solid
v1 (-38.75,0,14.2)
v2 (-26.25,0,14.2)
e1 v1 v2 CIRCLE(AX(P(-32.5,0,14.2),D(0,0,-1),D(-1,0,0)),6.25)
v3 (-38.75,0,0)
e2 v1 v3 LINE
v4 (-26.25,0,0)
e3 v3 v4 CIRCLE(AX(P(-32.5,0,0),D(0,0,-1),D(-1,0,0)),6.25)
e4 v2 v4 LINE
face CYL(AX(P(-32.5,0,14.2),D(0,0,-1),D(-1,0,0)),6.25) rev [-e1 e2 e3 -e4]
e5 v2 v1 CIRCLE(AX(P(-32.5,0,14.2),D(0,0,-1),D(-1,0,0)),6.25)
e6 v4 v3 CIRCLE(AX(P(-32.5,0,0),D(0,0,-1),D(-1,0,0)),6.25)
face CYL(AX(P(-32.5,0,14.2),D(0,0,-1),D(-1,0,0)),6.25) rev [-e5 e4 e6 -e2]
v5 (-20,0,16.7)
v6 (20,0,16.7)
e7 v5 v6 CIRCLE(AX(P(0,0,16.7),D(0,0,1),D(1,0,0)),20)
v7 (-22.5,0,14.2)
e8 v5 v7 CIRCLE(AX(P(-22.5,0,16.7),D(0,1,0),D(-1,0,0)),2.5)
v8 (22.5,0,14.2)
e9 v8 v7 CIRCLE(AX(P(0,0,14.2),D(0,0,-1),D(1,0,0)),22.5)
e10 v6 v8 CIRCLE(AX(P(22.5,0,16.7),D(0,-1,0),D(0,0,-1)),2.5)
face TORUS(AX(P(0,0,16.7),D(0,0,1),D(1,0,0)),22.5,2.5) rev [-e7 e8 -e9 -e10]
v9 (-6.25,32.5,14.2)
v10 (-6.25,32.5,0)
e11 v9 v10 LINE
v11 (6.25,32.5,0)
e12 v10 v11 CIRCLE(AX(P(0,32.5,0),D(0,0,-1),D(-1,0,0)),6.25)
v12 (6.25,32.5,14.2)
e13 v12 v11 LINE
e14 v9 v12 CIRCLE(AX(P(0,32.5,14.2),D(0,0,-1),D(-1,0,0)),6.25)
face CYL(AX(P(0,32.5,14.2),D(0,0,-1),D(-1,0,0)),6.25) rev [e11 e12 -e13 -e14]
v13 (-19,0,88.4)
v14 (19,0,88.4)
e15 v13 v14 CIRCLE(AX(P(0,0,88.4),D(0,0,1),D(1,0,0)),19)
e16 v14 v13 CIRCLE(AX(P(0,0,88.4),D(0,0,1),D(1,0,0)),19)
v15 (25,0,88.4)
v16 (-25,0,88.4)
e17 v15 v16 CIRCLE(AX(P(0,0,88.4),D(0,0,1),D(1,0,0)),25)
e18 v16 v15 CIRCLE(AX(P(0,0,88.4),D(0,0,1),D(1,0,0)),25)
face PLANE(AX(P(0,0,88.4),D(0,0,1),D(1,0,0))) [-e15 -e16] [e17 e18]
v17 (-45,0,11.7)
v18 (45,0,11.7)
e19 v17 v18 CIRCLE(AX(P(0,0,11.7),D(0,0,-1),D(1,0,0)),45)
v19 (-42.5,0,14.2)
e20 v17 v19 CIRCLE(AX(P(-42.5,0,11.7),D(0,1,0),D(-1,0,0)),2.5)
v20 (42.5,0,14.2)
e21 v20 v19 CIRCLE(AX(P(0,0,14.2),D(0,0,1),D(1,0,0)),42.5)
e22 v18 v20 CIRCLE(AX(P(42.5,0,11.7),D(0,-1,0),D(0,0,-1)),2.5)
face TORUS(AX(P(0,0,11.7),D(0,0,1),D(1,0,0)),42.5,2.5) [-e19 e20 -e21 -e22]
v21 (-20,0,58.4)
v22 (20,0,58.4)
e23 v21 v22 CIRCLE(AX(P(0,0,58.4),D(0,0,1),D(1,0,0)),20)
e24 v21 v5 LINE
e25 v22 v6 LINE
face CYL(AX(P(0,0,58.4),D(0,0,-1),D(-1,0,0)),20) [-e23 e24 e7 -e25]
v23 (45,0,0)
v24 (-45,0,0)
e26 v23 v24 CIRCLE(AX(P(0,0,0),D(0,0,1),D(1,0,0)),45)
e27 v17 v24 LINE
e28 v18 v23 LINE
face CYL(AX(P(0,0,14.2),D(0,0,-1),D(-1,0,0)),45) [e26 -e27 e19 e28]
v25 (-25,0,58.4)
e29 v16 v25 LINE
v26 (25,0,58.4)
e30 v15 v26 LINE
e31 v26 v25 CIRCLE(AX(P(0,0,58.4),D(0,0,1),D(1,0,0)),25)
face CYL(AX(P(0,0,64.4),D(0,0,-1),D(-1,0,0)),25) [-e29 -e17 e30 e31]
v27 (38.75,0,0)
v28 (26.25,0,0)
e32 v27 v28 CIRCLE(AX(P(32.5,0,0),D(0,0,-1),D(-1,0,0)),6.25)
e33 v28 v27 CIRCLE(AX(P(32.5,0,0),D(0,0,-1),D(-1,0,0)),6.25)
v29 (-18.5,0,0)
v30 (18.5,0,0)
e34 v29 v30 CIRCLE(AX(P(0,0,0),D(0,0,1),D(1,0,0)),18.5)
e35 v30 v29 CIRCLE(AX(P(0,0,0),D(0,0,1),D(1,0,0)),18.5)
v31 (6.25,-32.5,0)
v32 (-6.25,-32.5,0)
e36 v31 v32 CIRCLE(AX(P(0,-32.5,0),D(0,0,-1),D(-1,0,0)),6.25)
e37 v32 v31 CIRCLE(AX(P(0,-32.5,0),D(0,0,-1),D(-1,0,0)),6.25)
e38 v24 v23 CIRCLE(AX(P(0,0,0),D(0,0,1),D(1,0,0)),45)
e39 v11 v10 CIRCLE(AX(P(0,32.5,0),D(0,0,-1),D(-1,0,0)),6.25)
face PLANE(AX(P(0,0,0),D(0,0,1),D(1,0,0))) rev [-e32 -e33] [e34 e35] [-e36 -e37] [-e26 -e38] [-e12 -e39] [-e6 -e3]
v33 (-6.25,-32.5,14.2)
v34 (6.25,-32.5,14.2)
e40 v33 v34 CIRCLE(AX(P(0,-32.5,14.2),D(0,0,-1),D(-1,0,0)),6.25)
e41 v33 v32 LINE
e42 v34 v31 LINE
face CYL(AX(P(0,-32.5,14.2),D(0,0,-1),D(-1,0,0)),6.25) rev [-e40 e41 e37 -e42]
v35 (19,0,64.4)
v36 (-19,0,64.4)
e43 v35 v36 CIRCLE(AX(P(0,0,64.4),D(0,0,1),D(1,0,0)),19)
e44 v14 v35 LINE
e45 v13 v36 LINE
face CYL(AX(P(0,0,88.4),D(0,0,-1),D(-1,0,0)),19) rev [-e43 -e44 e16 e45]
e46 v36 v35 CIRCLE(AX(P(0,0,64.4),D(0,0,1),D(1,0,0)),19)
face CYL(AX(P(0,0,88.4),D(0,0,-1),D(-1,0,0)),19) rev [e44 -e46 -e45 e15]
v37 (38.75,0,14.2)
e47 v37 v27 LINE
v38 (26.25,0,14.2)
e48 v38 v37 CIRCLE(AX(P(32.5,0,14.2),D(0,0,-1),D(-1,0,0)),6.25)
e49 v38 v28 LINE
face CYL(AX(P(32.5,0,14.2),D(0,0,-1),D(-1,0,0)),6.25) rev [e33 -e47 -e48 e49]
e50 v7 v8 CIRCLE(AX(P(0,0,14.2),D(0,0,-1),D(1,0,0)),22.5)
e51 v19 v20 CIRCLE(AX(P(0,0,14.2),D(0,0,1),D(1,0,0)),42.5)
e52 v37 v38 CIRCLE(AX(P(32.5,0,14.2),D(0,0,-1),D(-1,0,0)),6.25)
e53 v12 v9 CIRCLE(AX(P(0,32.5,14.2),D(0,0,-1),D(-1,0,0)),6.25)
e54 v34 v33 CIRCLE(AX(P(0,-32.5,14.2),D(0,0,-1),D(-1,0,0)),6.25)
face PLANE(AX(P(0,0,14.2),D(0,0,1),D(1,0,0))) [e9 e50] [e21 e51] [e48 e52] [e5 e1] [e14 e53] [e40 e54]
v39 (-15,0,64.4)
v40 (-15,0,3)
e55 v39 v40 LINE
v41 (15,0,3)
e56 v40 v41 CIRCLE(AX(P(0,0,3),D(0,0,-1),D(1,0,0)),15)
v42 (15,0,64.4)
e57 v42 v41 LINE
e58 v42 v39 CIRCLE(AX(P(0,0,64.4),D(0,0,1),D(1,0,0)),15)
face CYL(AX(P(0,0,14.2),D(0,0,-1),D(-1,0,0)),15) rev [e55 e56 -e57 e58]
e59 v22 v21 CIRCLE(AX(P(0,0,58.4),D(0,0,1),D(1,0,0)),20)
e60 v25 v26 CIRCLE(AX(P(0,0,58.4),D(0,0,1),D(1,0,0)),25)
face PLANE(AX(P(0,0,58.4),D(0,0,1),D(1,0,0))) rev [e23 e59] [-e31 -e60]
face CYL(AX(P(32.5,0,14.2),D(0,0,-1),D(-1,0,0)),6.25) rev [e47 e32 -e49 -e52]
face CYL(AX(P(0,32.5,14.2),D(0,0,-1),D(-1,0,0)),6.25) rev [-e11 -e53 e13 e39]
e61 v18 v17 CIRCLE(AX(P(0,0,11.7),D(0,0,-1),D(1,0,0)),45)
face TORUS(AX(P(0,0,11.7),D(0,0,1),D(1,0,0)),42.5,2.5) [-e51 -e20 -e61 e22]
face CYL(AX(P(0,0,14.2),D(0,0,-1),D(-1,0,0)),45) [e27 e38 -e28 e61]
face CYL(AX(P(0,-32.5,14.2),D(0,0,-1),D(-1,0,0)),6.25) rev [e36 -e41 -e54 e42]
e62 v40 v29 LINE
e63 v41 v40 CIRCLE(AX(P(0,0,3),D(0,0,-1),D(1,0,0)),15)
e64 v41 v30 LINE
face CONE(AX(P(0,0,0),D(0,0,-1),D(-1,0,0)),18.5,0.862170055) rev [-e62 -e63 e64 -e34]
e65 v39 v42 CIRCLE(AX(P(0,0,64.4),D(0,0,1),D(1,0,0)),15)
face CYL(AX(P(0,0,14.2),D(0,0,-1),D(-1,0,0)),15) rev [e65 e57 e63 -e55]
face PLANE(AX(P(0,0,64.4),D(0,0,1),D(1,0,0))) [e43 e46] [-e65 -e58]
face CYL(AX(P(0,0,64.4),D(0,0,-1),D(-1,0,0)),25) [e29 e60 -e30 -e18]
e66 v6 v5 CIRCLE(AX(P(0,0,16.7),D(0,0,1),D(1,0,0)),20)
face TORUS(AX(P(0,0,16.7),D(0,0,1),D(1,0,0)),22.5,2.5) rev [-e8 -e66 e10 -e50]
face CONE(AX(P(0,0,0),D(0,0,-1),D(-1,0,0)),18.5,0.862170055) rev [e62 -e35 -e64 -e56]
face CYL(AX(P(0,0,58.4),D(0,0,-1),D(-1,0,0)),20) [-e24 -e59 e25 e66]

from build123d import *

# Parameters (mm, degrees)
FLANGE_PROFILE_SKETCH_R       = 45
FLANGE_PROFILE_SKETCH_R_2     = 15
FLANGE_90_DEPTH               = 14.2
FLANGE_HOLES_SKETCH_R         = 6.25
FLANGE_HOLES_4X_12_5_DEPTH    = 66.204601065
FLANGE_CHAMFER_SIZE           = 3
FLANGE_CHAMFER_SIZE2          = 3.5
NECK_PROFILE_SKETCH_R         = 20
NECK_PROFILE_SKETCH_R_2       = 15
NECK_40_DEPTH                 = 44.2
FLANGE_EDGE_FILLET_R2_5_R     = 2.5
COLLAR_PROFILE_SKETCH_R       = 25
COLLAR_PROFILE_SKETCH_R_2     = 15
COLLAR_50_DEPTH               = 6
END_SLEEVE_PROFILE_SKETCH_R   = 25
END_SLEEVE_PROFILE_SKETCH_R_2 = 19
END_SLEEVE_50_BORE_38_DEPTH   = 24
NECK_ROOT_FILLET_R2_5_R       = 2.5


with BuildPart() as part:
    # Flange Profile Sketch → Flange Ø90 (new body)
    with BuildSketch(Plane.XY):
        Circle(FLANGE_PROFILE_SKETCH_R)
        Circle(FLANGE_PROFILE_SKETCH_R_2, mode=Mode.SUBTRACT)
    extrude(amount=FLANGE_90_DEPTH)

    # Flange Holes Sketch → Flange Holes 4xØ12.5 (cut, through all)
    with BuildSketch(Plane(origin=(0, 0, 0), x_dir=(-1, 0, 0), z_dir=(0, 0, -1))):
        with Locations((-32.5, 0)):
            Circle(FLANGE_HOLES_SKETCH_R)
        with Locations((32.5, 0)):
            Circle(FLANGE_HOLES_SKETCH_R)
        with Locations((0, -32.5)):
            Circle(FLANGE_HOLES_SKETCH_R)
        with Locations((0, 32.5)):
            Circle(FLANGE_HOLES_SKETCH_R)
    extrude(amount=-FLANGE_HOLES_4X_12_5_DEPTH, mode=Mode.SUBTRACT)

    # Flange Chamfer
    flange_chamfer_edges = [part.edges().sort_by_distance(p)[0] for p in [
        (-15, 0, 0),
    ]]
    flange_chamfer_side = [part.faces().sort_by_distance(p)[0] for p in [
        (-15, 0, 7.1),
    ]]
    chamfer(flange_chamfer_edges, length=FLANGE_CHAMFER_SIZE, length2=FLANGE_CHAMFER_SIZE2, reference=flange_chamfer_side[0])

    # Neck Profile Sketch → Neck Ø40 (add)
    with BuildSketch(Plane.XY.offset(14.2)):
        Circle(NECK_PROFILE_SKETCH_R)
        Circle(NECK_PROFILE_SKETCH_R_2, mode=Mode.SUBTRACT)
    extrude(amount=NECK_40_DEPTH)

    # Flange Edge Fillet R2.5
    flange_edge_fillet_r2_5_edges = [part.edges().sort_by_distance(p)[0] for p in [
        (-45, 0, 14.2),
    ]]
    fillet(flange_edge_fillet_r2_5_edges, radius=FLANGE_EDGE_FILLET_R2_5_R)

    # Collar Profile Sketch → Collar Ø50 (add)
    with BuildSketch(Plane.XY.offset(58.4)):
        Circle(COLLAR_PROFILE_SKETCH_R)
        Circle(COLLAR_PROFILE_SKETCH_R_2, mode=Mode.SUBTRACT)
    extrude(amount=COLLAR_50_DEPTH)

    # End Sleeve Profile Sketch → End Sleeve Ø50 Bore Ø38 (add)
    with BuildSketch(Plane.XY.offset(64.4)):
        Circle(END_SLEEVE_PROFILE_SKETCH_R)
        Circle(END_SLEEVE_PROFILE_SKETCH_R_2, mode=Mode.SUBTRACT)
    extrude(amount=END_SLEEVE_50_BORE_38_DEPTH)

    # Neck Root Fillet R2.5
    neck_root_fillet_r2_5_edges = [part.edges().sort_by_distance(p)[0] for p in [
        (-20, 0, 14.2),
    ]]
    fillet(neck_root_fillet_r2_5_edges, radius=NECK_ROOT_FILLET_R2_5_R)


solid = part.part
